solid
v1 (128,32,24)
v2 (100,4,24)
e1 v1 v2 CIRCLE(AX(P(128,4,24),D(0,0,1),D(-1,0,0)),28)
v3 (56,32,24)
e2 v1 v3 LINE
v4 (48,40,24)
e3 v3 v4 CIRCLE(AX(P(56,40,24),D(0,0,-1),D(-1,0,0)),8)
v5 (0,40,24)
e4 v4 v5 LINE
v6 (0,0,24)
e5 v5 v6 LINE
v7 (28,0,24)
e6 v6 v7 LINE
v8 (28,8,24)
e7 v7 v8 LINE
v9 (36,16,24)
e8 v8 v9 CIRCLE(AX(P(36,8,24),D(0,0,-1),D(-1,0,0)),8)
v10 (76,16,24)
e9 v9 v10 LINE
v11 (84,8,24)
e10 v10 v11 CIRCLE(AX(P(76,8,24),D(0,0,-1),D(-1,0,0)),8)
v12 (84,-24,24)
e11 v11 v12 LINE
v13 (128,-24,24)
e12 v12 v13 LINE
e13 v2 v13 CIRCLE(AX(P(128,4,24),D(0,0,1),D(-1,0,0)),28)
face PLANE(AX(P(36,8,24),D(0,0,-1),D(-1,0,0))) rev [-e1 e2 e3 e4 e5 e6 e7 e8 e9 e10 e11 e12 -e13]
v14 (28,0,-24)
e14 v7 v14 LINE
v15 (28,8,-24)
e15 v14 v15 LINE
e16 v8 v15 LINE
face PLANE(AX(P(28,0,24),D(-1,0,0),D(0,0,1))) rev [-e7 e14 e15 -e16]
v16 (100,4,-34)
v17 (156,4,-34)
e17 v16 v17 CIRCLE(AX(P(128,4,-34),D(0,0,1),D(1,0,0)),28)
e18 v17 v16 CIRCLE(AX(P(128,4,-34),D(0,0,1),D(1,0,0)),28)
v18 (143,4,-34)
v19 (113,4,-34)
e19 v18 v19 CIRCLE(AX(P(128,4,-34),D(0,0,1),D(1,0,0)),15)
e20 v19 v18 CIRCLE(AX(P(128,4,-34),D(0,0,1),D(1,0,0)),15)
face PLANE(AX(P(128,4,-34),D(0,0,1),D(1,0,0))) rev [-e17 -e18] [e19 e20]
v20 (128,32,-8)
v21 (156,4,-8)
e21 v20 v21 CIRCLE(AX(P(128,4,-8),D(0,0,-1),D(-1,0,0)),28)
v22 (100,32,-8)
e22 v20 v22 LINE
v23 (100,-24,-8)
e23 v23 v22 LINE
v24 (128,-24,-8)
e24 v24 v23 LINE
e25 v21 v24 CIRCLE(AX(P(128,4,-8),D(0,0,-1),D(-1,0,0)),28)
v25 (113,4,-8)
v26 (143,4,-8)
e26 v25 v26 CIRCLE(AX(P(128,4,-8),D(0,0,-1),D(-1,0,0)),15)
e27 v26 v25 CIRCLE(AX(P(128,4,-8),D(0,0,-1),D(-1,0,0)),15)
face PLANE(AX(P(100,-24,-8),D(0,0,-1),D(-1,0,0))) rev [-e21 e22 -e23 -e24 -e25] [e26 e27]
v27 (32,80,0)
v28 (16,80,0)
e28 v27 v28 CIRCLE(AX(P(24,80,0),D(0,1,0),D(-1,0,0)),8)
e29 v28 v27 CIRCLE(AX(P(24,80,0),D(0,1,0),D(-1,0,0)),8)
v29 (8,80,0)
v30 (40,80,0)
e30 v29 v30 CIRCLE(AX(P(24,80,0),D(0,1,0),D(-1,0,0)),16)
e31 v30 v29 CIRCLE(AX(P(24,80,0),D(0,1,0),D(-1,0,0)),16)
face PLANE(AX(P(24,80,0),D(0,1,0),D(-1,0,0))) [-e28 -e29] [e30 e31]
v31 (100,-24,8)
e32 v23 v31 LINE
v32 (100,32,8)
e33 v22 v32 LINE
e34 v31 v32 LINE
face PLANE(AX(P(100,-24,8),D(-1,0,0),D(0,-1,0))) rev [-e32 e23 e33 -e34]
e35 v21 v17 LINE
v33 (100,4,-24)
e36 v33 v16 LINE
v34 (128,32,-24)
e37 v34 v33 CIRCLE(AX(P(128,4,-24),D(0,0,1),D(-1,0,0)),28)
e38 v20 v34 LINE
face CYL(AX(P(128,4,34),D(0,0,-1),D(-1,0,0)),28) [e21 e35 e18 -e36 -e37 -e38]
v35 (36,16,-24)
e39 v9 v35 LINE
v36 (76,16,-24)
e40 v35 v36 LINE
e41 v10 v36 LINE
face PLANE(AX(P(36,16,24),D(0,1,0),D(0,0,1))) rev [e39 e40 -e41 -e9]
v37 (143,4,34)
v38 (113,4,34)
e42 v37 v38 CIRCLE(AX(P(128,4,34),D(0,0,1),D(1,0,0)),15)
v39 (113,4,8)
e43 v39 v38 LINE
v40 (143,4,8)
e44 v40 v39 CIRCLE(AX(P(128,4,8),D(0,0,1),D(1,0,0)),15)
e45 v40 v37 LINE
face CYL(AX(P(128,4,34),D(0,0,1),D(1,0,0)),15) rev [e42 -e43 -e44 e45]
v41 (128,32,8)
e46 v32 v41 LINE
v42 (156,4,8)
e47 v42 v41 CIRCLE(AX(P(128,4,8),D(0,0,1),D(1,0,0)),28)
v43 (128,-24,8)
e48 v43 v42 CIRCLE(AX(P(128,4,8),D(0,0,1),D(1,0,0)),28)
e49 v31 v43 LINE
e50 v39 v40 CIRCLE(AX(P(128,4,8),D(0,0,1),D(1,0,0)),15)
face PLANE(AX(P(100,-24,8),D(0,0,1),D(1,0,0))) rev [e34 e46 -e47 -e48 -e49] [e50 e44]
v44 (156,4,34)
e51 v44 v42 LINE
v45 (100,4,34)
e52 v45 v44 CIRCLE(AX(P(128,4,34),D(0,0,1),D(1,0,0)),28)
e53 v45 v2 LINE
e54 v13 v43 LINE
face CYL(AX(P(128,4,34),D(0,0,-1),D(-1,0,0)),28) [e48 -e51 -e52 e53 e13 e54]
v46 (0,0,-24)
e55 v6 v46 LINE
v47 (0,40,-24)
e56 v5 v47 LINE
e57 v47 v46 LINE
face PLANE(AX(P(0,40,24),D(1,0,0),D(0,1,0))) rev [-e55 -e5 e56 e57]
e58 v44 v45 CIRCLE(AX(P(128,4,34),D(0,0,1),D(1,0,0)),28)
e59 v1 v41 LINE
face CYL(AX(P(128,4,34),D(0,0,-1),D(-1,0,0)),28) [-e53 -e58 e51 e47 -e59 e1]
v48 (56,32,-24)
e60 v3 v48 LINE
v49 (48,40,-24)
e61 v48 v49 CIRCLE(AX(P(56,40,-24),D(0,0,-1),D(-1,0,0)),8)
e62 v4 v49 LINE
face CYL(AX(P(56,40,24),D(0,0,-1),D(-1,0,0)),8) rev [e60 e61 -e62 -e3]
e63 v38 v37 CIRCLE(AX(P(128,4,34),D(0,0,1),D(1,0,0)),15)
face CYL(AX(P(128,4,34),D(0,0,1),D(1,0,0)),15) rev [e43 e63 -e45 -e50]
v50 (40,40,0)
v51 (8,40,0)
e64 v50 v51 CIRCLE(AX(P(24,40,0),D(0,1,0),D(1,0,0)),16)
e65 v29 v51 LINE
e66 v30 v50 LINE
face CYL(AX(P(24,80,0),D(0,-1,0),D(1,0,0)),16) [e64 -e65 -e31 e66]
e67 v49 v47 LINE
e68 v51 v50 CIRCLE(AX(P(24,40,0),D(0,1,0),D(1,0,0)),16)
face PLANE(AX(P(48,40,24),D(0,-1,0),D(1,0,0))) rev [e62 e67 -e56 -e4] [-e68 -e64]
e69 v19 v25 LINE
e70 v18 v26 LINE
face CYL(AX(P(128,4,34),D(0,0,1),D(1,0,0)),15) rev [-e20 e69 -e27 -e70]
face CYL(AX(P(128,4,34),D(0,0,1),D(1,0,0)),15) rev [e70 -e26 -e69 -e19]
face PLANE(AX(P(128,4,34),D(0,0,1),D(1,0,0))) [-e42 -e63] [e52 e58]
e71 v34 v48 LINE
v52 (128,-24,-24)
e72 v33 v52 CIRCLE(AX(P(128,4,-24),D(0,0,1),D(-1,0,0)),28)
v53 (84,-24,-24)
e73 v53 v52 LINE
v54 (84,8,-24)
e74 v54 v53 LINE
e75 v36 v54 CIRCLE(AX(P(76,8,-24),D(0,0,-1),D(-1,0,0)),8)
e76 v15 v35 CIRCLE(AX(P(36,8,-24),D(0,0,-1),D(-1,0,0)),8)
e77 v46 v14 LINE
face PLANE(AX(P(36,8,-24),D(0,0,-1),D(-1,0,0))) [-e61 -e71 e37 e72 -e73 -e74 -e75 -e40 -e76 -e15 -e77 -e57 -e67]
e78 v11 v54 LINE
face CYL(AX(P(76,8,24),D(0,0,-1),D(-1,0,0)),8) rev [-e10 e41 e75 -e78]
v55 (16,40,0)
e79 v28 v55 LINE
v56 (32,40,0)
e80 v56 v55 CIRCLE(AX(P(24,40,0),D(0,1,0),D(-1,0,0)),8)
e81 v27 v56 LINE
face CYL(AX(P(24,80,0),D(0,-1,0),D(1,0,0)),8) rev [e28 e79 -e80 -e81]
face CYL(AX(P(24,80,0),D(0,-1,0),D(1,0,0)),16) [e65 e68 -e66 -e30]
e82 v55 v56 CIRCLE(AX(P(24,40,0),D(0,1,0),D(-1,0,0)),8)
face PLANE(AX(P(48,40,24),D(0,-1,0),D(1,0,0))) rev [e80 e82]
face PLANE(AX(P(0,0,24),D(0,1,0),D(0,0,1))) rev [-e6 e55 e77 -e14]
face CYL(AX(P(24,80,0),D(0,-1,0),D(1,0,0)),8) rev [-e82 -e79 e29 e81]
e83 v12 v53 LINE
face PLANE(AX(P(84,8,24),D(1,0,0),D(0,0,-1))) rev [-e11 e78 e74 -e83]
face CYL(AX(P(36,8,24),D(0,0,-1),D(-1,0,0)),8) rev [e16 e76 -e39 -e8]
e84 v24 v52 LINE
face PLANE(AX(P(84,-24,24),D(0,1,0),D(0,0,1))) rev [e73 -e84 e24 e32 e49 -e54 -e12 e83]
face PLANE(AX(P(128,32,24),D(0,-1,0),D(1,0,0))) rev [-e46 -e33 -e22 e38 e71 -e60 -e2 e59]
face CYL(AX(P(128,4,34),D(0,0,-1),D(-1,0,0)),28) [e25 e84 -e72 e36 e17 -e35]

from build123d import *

# Parameters (mm, degrees)
ARM_BODY_DEPTH          = 24
BUSHING_BOSS_SKETCH_R   = 16
BUSHING_BOSS_SKETCH_R_2 = 8
BUSHING_BOSS_32_DEPTH   = 40
PIVOT_LUG_SKETCH_R      = 28
PIVOT_LUG_56_DEPTH      = 34
CLEVIS_SLOT_SKETCH_W    = 56
CLEVIS_SLOT_SKETCH_H    = 16
CLEVIS_SLOT_16MM_DEPTH  = 170.198108736
PIVOT_BORE_30_D         = 30


with BuildPart() as part:
    # Arm Profile Sketch → Arm Body (new, symmetric)
    with BuildSketch(Plane.XY):
        with BuildLine():
            Line((0, 0), (28, 0))
            Line((28, 0), (28, 8))
            ThreePointArc((28, 8), (30.343145751, 13.656854249), (36, 16))
            Line((36, 16), (76, 16))
            ThreePointArc((76, 16), (81.656854249, 13.656854249), (84, 8))
            Line((84, 8), (84, -24))
            Line((84, -24), (128, -24))
            Line((128, -24), (128, 32))
            Line((128, 32), (56, 32))
            ThreePointArc((56, 32), (50.343145751, 34.343145751), (48, 40))
            Line((48, 40), (0, 40))
            Line((0, 40), (0, 0))
        make_face()
    extrude(amount=ARM_BODY_DEPTH, both=True)

    # Bushing Boss Sketch → Bushing Boss Ø32 (add)
    with BuildSketch(Plane(origin=(0, 40, 0), x_dir=(1, 0, 0), z_dir=(0, 1, 0))):
        with Locations((24, 0)):
            Circle(BUSHING_BOSS_SKETCH_R)
        with Locations(Location((24, 0, 0), (0, 0, 180))):
            Circle(BUSHING_BOSS_SKETCH_R_2, mode=Mode.SUBTRACT)
    extrude(amount=BUSHING_BOSS_32_DEPTH)

    # Pivot Lug Sketch → Pivot Lug Ø56 (add, symmetric)
    with BuildSketch(Plane.XY):
        with Locations((128, 4)):
            Circle(PIVOT_LUG_SKETCH_R)
    extrude(amount=PIVOT_LUG_56_DEPTH, both=True)

    # Clevis Slot Sketch → Clevis Slot 16mm (cut, through all)
    with BuildSketch(Plane(origin=(0, 32, 0), x_dir=(1, 0, 0), z_dir=(0, 1, 0))):
        with Locations((128, 0)):
            Rectangle(CLEVIS_SLOT_SKETCH_W, CLEVIS_SLOT_SKETCH_H)
    extrude(amount=-CLEVIS_SLOT_16MM_DEPTH, mode=Mode.SUBTRACT)

    # Pivot Bore Ø30 (through all)
    with Locations(Plane.XY.offset(34)):
        with Locations((128, 4)):
            Hole(PIVOT_BORE_30_D / 2)


solid = part.part
